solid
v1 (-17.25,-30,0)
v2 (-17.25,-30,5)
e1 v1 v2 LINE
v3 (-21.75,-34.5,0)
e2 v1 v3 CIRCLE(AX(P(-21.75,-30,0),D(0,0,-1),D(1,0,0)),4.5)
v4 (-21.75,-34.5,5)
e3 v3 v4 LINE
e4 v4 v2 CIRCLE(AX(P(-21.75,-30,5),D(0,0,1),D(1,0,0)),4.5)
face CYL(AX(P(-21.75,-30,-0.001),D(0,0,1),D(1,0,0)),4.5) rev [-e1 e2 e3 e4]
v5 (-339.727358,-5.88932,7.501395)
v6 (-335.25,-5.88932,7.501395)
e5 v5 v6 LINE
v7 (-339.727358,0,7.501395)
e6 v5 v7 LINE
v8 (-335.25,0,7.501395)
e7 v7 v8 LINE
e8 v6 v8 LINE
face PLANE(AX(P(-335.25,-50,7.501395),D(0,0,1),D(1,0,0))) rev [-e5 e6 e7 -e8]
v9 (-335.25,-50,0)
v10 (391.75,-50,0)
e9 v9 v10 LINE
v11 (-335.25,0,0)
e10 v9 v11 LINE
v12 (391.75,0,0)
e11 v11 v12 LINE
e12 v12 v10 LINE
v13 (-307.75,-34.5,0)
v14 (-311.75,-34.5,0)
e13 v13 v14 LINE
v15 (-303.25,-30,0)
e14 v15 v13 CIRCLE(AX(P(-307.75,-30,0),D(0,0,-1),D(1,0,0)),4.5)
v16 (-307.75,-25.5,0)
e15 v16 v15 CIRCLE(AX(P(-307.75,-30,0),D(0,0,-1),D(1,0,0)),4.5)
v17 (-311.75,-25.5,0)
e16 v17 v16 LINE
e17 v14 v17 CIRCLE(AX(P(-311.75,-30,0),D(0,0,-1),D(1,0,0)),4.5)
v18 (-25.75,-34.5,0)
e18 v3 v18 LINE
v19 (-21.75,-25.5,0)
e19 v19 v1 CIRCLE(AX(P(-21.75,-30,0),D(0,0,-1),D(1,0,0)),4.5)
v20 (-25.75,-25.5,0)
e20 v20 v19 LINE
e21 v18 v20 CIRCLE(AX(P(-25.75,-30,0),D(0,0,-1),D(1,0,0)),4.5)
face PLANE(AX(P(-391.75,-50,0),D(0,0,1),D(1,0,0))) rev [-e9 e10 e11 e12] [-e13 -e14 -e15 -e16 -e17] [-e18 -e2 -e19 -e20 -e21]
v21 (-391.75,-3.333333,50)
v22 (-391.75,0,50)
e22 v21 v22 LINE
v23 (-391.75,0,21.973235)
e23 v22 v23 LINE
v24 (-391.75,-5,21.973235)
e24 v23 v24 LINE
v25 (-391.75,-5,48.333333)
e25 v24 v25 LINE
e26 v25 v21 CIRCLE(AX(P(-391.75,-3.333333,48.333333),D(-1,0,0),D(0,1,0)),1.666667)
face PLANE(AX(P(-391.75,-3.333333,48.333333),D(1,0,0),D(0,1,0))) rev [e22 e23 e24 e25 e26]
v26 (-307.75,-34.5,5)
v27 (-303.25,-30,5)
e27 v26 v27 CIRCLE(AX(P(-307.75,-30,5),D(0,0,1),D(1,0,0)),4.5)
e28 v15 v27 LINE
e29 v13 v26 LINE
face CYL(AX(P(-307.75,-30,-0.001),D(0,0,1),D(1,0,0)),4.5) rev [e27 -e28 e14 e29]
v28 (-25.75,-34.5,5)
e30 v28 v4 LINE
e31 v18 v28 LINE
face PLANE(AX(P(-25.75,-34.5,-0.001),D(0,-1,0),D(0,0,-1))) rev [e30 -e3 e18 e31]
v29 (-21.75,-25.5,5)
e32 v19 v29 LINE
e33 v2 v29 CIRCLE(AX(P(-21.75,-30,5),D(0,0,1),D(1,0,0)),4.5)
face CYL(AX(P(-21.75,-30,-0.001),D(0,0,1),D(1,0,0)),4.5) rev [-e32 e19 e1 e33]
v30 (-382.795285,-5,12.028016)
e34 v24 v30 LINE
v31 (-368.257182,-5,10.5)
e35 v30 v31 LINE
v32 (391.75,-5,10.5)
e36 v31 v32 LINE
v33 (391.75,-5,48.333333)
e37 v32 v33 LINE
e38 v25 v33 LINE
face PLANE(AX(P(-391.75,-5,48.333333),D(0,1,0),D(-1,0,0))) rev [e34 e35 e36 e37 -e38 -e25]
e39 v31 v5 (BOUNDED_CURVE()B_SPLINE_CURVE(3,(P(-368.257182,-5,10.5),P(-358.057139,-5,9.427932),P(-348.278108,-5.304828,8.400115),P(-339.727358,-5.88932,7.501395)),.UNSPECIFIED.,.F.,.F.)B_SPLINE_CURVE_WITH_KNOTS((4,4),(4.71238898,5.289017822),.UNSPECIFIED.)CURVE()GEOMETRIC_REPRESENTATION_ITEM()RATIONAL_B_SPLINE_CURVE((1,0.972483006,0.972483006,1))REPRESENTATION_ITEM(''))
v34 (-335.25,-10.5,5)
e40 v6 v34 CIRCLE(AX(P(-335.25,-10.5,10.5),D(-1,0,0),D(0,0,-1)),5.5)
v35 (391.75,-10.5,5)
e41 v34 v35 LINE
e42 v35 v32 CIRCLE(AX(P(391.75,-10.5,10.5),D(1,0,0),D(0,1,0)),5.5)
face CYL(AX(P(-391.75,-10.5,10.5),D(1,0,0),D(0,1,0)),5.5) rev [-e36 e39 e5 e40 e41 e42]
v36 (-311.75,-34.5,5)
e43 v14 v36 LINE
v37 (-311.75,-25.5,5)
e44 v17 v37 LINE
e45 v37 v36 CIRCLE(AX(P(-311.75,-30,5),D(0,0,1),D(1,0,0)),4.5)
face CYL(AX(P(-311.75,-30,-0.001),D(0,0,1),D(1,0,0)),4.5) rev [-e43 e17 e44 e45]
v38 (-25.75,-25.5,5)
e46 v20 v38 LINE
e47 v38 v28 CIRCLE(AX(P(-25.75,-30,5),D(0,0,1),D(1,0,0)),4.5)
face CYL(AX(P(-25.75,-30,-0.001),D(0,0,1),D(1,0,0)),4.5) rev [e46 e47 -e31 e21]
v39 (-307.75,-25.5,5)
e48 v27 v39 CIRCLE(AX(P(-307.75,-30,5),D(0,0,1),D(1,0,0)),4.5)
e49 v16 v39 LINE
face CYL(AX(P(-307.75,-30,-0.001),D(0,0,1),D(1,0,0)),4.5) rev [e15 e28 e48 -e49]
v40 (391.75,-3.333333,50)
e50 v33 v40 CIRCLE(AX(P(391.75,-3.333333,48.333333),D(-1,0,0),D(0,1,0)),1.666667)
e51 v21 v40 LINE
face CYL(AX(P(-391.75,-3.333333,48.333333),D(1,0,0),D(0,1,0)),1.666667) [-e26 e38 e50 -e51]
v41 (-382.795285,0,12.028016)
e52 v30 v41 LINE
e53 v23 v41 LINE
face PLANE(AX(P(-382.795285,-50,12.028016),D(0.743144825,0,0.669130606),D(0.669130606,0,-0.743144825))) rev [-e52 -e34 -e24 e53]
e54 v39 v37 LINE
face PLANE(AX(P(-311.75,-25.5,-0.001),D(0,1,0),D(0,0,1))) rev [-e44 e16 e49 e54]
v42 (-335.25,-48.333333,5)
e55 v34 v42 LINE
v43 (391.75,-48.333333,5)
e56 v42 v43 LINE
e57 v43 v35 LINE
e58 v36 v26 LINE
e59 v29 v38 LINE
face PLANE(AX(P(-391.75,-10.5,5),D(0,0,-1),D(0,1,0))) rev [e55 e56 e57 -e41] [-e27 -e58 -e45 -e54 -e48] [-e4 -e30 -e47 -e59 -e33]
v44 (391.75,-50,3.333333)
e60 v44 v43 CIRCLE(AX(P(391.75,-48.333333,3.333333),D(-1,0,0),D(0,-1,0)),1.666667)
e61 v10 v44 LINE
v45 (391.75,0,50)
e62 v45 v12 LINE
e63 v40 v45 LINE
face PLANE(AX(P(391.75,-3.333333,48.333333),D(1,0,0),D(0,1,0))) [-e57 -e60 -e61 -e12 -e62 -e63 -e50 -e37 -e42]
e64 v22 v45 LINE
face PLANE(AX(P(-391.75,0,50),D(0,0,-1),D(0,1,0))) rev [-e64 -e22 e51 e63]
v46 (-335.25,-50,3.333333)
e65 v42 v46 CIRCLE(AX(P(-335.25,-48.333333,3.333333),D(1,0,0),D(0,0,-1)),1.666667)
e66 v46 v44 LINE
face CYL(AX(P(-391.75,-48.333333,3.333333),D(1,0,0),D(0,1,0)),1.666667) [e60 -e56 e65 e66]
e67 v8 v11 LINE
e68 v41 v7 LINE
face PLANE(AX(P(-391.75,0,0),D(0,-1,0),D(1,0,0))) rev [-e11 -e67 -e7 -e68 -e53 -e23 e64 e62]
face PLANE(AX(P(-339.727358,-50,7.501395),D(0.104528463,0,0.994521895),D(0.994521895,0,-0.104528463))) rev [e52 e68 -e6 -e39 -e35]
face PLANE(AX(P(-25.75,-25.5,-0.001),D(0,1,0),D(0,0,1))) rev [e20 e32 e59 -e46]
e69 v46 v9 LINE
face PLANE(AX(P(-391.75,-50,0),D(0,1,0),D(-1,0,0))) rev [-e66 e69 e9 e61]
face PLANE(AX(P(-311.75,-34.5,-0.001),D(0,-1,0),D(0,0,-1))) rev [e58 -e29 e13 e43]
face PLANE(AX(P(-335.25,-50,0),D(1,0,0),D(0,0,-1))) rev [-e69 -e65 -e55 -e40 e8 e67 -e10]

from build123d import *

# Parameters (mm, degrees)
GBT706_2008_050_5_1_DEPTH = 783.5
CUT_EXTRUDE_1_DEPTH       = 399.080472392
CUT_EXTRUDE_2_REACH       = 399.483


with BuildPart() as part:
    # Sketch1 → Gbt706-2008 热轧等边角钢 050×5(1) (new body)
    with BuildSketch(Plane(origin=(391.75, 0, 0), x_dir=(0, -1, 0), z_dir=(-1, 0, 0))):
        with BuildLine():
            Line((0, 0), (0, 50))
            Line((0, 50), (3.333333333, 50))
            ThreePointArc((3.333333333, 50), (4.511844635, 49.511844635), (5, 48.333333333))
            Line((5, 48.333333333), (5, 10.5))
            ThreePointArc((5, 10.5), (6.610912703, 6.610912703), (10.5, 5))
            Line((10.5, 5), (48.333333333, 5))
            ThreePointArc((48.333333333, 5), (49.511844635, 4.511844635), (50, 3.333333333))
            Line((50, 3.333333333), (50, 0))
            Line((50, 0), (0, 0))
        make_face()
    extrude(amount=GBT706_2008_050_5_1_DEPTH)

    # 草图2 → 切除-拉伸1 (cut, through all)
    with BuildSketch(Plane(origin=(0, 0, 0), x_dir=(1, 0, 0), z_dir=(0, 1, 0))):
        Polygon((-335.25, 0), (-335.25, -7.501394609), (-339.727357684, -7.501394609), (-382.795284633, -12.028016136), (-391.75, -21.973235089), (-391.75, -52.501394609), (-406.75, -52.501394609), (-406.75, 7.498605391), (-335.25, 7.498605391), align=None)
    extrude(amount=-CUT_EXTRUDE_1_DEPTH, mode=Mode.SUBTRACT)

    # 草图3 → 切除-拉伸2 (cut, up to next)
    with BuildSketch(Plane.XY.offset(5), mode=Mode.PRIVATE) as cut_extrude_2_sk1:
        with BuildLine():
            Line((-25.75, -25.5), (-21.75, -25.5))
            ThreePointArc((-21.75, -25.5), (-17.25, -30), (-21.75, -34.5))
            Line((-21.75, -34.5), (-25.75, -34.5))
            ThreePointArc((-25.75, -34.5), (-30.25, -30), (-25.75, -25.5))
        make_face()
    cut_extrude_2_tool1 = extrude(cut_extrude_2_sk1.sketch, amount=-CUT_EXTRUDE_2_REACH, mode=Mode.PRIVATE) & part.part
    # 草图3 → 切除-拉伸2 (cut, up to next)
    with BuildSketch(Plane.XY.offset(5), mode=Mode.PRIVATE) as cut_extrude_2_sk2:
        with BuildLine():
            Line((-311.75, -25.5), (-307.75, -25.5))
            ThreePointArc((-307.75, -25.5), (-303.25, -30), (-307.75, -34.5))
            Line((-307.75, -34.5), (-311.75, -34.5))
            ThreePointArc((-311.75, -34.5), (-316.25, -30), (-311.75, -25.5))
        make_face()
    cut_extrude_2_tool2 = extrude(cut_extrude_2_sk2.sketch, amount=-CUT_EXTRUDE_2_REACH, mode=Mode.PRIVATE) & part.part
    add(cut_extrude_2_tool1.solids().sort_by_distance((-23.75, -30, 5))[0], mode=Mode.SUBTRACT)
    add(cut_extrude_2_tool2.solids().sort_by_distance((-309.75, -30, 5))[0], mode=Mode.SUBTRACT)


solid = part.part
